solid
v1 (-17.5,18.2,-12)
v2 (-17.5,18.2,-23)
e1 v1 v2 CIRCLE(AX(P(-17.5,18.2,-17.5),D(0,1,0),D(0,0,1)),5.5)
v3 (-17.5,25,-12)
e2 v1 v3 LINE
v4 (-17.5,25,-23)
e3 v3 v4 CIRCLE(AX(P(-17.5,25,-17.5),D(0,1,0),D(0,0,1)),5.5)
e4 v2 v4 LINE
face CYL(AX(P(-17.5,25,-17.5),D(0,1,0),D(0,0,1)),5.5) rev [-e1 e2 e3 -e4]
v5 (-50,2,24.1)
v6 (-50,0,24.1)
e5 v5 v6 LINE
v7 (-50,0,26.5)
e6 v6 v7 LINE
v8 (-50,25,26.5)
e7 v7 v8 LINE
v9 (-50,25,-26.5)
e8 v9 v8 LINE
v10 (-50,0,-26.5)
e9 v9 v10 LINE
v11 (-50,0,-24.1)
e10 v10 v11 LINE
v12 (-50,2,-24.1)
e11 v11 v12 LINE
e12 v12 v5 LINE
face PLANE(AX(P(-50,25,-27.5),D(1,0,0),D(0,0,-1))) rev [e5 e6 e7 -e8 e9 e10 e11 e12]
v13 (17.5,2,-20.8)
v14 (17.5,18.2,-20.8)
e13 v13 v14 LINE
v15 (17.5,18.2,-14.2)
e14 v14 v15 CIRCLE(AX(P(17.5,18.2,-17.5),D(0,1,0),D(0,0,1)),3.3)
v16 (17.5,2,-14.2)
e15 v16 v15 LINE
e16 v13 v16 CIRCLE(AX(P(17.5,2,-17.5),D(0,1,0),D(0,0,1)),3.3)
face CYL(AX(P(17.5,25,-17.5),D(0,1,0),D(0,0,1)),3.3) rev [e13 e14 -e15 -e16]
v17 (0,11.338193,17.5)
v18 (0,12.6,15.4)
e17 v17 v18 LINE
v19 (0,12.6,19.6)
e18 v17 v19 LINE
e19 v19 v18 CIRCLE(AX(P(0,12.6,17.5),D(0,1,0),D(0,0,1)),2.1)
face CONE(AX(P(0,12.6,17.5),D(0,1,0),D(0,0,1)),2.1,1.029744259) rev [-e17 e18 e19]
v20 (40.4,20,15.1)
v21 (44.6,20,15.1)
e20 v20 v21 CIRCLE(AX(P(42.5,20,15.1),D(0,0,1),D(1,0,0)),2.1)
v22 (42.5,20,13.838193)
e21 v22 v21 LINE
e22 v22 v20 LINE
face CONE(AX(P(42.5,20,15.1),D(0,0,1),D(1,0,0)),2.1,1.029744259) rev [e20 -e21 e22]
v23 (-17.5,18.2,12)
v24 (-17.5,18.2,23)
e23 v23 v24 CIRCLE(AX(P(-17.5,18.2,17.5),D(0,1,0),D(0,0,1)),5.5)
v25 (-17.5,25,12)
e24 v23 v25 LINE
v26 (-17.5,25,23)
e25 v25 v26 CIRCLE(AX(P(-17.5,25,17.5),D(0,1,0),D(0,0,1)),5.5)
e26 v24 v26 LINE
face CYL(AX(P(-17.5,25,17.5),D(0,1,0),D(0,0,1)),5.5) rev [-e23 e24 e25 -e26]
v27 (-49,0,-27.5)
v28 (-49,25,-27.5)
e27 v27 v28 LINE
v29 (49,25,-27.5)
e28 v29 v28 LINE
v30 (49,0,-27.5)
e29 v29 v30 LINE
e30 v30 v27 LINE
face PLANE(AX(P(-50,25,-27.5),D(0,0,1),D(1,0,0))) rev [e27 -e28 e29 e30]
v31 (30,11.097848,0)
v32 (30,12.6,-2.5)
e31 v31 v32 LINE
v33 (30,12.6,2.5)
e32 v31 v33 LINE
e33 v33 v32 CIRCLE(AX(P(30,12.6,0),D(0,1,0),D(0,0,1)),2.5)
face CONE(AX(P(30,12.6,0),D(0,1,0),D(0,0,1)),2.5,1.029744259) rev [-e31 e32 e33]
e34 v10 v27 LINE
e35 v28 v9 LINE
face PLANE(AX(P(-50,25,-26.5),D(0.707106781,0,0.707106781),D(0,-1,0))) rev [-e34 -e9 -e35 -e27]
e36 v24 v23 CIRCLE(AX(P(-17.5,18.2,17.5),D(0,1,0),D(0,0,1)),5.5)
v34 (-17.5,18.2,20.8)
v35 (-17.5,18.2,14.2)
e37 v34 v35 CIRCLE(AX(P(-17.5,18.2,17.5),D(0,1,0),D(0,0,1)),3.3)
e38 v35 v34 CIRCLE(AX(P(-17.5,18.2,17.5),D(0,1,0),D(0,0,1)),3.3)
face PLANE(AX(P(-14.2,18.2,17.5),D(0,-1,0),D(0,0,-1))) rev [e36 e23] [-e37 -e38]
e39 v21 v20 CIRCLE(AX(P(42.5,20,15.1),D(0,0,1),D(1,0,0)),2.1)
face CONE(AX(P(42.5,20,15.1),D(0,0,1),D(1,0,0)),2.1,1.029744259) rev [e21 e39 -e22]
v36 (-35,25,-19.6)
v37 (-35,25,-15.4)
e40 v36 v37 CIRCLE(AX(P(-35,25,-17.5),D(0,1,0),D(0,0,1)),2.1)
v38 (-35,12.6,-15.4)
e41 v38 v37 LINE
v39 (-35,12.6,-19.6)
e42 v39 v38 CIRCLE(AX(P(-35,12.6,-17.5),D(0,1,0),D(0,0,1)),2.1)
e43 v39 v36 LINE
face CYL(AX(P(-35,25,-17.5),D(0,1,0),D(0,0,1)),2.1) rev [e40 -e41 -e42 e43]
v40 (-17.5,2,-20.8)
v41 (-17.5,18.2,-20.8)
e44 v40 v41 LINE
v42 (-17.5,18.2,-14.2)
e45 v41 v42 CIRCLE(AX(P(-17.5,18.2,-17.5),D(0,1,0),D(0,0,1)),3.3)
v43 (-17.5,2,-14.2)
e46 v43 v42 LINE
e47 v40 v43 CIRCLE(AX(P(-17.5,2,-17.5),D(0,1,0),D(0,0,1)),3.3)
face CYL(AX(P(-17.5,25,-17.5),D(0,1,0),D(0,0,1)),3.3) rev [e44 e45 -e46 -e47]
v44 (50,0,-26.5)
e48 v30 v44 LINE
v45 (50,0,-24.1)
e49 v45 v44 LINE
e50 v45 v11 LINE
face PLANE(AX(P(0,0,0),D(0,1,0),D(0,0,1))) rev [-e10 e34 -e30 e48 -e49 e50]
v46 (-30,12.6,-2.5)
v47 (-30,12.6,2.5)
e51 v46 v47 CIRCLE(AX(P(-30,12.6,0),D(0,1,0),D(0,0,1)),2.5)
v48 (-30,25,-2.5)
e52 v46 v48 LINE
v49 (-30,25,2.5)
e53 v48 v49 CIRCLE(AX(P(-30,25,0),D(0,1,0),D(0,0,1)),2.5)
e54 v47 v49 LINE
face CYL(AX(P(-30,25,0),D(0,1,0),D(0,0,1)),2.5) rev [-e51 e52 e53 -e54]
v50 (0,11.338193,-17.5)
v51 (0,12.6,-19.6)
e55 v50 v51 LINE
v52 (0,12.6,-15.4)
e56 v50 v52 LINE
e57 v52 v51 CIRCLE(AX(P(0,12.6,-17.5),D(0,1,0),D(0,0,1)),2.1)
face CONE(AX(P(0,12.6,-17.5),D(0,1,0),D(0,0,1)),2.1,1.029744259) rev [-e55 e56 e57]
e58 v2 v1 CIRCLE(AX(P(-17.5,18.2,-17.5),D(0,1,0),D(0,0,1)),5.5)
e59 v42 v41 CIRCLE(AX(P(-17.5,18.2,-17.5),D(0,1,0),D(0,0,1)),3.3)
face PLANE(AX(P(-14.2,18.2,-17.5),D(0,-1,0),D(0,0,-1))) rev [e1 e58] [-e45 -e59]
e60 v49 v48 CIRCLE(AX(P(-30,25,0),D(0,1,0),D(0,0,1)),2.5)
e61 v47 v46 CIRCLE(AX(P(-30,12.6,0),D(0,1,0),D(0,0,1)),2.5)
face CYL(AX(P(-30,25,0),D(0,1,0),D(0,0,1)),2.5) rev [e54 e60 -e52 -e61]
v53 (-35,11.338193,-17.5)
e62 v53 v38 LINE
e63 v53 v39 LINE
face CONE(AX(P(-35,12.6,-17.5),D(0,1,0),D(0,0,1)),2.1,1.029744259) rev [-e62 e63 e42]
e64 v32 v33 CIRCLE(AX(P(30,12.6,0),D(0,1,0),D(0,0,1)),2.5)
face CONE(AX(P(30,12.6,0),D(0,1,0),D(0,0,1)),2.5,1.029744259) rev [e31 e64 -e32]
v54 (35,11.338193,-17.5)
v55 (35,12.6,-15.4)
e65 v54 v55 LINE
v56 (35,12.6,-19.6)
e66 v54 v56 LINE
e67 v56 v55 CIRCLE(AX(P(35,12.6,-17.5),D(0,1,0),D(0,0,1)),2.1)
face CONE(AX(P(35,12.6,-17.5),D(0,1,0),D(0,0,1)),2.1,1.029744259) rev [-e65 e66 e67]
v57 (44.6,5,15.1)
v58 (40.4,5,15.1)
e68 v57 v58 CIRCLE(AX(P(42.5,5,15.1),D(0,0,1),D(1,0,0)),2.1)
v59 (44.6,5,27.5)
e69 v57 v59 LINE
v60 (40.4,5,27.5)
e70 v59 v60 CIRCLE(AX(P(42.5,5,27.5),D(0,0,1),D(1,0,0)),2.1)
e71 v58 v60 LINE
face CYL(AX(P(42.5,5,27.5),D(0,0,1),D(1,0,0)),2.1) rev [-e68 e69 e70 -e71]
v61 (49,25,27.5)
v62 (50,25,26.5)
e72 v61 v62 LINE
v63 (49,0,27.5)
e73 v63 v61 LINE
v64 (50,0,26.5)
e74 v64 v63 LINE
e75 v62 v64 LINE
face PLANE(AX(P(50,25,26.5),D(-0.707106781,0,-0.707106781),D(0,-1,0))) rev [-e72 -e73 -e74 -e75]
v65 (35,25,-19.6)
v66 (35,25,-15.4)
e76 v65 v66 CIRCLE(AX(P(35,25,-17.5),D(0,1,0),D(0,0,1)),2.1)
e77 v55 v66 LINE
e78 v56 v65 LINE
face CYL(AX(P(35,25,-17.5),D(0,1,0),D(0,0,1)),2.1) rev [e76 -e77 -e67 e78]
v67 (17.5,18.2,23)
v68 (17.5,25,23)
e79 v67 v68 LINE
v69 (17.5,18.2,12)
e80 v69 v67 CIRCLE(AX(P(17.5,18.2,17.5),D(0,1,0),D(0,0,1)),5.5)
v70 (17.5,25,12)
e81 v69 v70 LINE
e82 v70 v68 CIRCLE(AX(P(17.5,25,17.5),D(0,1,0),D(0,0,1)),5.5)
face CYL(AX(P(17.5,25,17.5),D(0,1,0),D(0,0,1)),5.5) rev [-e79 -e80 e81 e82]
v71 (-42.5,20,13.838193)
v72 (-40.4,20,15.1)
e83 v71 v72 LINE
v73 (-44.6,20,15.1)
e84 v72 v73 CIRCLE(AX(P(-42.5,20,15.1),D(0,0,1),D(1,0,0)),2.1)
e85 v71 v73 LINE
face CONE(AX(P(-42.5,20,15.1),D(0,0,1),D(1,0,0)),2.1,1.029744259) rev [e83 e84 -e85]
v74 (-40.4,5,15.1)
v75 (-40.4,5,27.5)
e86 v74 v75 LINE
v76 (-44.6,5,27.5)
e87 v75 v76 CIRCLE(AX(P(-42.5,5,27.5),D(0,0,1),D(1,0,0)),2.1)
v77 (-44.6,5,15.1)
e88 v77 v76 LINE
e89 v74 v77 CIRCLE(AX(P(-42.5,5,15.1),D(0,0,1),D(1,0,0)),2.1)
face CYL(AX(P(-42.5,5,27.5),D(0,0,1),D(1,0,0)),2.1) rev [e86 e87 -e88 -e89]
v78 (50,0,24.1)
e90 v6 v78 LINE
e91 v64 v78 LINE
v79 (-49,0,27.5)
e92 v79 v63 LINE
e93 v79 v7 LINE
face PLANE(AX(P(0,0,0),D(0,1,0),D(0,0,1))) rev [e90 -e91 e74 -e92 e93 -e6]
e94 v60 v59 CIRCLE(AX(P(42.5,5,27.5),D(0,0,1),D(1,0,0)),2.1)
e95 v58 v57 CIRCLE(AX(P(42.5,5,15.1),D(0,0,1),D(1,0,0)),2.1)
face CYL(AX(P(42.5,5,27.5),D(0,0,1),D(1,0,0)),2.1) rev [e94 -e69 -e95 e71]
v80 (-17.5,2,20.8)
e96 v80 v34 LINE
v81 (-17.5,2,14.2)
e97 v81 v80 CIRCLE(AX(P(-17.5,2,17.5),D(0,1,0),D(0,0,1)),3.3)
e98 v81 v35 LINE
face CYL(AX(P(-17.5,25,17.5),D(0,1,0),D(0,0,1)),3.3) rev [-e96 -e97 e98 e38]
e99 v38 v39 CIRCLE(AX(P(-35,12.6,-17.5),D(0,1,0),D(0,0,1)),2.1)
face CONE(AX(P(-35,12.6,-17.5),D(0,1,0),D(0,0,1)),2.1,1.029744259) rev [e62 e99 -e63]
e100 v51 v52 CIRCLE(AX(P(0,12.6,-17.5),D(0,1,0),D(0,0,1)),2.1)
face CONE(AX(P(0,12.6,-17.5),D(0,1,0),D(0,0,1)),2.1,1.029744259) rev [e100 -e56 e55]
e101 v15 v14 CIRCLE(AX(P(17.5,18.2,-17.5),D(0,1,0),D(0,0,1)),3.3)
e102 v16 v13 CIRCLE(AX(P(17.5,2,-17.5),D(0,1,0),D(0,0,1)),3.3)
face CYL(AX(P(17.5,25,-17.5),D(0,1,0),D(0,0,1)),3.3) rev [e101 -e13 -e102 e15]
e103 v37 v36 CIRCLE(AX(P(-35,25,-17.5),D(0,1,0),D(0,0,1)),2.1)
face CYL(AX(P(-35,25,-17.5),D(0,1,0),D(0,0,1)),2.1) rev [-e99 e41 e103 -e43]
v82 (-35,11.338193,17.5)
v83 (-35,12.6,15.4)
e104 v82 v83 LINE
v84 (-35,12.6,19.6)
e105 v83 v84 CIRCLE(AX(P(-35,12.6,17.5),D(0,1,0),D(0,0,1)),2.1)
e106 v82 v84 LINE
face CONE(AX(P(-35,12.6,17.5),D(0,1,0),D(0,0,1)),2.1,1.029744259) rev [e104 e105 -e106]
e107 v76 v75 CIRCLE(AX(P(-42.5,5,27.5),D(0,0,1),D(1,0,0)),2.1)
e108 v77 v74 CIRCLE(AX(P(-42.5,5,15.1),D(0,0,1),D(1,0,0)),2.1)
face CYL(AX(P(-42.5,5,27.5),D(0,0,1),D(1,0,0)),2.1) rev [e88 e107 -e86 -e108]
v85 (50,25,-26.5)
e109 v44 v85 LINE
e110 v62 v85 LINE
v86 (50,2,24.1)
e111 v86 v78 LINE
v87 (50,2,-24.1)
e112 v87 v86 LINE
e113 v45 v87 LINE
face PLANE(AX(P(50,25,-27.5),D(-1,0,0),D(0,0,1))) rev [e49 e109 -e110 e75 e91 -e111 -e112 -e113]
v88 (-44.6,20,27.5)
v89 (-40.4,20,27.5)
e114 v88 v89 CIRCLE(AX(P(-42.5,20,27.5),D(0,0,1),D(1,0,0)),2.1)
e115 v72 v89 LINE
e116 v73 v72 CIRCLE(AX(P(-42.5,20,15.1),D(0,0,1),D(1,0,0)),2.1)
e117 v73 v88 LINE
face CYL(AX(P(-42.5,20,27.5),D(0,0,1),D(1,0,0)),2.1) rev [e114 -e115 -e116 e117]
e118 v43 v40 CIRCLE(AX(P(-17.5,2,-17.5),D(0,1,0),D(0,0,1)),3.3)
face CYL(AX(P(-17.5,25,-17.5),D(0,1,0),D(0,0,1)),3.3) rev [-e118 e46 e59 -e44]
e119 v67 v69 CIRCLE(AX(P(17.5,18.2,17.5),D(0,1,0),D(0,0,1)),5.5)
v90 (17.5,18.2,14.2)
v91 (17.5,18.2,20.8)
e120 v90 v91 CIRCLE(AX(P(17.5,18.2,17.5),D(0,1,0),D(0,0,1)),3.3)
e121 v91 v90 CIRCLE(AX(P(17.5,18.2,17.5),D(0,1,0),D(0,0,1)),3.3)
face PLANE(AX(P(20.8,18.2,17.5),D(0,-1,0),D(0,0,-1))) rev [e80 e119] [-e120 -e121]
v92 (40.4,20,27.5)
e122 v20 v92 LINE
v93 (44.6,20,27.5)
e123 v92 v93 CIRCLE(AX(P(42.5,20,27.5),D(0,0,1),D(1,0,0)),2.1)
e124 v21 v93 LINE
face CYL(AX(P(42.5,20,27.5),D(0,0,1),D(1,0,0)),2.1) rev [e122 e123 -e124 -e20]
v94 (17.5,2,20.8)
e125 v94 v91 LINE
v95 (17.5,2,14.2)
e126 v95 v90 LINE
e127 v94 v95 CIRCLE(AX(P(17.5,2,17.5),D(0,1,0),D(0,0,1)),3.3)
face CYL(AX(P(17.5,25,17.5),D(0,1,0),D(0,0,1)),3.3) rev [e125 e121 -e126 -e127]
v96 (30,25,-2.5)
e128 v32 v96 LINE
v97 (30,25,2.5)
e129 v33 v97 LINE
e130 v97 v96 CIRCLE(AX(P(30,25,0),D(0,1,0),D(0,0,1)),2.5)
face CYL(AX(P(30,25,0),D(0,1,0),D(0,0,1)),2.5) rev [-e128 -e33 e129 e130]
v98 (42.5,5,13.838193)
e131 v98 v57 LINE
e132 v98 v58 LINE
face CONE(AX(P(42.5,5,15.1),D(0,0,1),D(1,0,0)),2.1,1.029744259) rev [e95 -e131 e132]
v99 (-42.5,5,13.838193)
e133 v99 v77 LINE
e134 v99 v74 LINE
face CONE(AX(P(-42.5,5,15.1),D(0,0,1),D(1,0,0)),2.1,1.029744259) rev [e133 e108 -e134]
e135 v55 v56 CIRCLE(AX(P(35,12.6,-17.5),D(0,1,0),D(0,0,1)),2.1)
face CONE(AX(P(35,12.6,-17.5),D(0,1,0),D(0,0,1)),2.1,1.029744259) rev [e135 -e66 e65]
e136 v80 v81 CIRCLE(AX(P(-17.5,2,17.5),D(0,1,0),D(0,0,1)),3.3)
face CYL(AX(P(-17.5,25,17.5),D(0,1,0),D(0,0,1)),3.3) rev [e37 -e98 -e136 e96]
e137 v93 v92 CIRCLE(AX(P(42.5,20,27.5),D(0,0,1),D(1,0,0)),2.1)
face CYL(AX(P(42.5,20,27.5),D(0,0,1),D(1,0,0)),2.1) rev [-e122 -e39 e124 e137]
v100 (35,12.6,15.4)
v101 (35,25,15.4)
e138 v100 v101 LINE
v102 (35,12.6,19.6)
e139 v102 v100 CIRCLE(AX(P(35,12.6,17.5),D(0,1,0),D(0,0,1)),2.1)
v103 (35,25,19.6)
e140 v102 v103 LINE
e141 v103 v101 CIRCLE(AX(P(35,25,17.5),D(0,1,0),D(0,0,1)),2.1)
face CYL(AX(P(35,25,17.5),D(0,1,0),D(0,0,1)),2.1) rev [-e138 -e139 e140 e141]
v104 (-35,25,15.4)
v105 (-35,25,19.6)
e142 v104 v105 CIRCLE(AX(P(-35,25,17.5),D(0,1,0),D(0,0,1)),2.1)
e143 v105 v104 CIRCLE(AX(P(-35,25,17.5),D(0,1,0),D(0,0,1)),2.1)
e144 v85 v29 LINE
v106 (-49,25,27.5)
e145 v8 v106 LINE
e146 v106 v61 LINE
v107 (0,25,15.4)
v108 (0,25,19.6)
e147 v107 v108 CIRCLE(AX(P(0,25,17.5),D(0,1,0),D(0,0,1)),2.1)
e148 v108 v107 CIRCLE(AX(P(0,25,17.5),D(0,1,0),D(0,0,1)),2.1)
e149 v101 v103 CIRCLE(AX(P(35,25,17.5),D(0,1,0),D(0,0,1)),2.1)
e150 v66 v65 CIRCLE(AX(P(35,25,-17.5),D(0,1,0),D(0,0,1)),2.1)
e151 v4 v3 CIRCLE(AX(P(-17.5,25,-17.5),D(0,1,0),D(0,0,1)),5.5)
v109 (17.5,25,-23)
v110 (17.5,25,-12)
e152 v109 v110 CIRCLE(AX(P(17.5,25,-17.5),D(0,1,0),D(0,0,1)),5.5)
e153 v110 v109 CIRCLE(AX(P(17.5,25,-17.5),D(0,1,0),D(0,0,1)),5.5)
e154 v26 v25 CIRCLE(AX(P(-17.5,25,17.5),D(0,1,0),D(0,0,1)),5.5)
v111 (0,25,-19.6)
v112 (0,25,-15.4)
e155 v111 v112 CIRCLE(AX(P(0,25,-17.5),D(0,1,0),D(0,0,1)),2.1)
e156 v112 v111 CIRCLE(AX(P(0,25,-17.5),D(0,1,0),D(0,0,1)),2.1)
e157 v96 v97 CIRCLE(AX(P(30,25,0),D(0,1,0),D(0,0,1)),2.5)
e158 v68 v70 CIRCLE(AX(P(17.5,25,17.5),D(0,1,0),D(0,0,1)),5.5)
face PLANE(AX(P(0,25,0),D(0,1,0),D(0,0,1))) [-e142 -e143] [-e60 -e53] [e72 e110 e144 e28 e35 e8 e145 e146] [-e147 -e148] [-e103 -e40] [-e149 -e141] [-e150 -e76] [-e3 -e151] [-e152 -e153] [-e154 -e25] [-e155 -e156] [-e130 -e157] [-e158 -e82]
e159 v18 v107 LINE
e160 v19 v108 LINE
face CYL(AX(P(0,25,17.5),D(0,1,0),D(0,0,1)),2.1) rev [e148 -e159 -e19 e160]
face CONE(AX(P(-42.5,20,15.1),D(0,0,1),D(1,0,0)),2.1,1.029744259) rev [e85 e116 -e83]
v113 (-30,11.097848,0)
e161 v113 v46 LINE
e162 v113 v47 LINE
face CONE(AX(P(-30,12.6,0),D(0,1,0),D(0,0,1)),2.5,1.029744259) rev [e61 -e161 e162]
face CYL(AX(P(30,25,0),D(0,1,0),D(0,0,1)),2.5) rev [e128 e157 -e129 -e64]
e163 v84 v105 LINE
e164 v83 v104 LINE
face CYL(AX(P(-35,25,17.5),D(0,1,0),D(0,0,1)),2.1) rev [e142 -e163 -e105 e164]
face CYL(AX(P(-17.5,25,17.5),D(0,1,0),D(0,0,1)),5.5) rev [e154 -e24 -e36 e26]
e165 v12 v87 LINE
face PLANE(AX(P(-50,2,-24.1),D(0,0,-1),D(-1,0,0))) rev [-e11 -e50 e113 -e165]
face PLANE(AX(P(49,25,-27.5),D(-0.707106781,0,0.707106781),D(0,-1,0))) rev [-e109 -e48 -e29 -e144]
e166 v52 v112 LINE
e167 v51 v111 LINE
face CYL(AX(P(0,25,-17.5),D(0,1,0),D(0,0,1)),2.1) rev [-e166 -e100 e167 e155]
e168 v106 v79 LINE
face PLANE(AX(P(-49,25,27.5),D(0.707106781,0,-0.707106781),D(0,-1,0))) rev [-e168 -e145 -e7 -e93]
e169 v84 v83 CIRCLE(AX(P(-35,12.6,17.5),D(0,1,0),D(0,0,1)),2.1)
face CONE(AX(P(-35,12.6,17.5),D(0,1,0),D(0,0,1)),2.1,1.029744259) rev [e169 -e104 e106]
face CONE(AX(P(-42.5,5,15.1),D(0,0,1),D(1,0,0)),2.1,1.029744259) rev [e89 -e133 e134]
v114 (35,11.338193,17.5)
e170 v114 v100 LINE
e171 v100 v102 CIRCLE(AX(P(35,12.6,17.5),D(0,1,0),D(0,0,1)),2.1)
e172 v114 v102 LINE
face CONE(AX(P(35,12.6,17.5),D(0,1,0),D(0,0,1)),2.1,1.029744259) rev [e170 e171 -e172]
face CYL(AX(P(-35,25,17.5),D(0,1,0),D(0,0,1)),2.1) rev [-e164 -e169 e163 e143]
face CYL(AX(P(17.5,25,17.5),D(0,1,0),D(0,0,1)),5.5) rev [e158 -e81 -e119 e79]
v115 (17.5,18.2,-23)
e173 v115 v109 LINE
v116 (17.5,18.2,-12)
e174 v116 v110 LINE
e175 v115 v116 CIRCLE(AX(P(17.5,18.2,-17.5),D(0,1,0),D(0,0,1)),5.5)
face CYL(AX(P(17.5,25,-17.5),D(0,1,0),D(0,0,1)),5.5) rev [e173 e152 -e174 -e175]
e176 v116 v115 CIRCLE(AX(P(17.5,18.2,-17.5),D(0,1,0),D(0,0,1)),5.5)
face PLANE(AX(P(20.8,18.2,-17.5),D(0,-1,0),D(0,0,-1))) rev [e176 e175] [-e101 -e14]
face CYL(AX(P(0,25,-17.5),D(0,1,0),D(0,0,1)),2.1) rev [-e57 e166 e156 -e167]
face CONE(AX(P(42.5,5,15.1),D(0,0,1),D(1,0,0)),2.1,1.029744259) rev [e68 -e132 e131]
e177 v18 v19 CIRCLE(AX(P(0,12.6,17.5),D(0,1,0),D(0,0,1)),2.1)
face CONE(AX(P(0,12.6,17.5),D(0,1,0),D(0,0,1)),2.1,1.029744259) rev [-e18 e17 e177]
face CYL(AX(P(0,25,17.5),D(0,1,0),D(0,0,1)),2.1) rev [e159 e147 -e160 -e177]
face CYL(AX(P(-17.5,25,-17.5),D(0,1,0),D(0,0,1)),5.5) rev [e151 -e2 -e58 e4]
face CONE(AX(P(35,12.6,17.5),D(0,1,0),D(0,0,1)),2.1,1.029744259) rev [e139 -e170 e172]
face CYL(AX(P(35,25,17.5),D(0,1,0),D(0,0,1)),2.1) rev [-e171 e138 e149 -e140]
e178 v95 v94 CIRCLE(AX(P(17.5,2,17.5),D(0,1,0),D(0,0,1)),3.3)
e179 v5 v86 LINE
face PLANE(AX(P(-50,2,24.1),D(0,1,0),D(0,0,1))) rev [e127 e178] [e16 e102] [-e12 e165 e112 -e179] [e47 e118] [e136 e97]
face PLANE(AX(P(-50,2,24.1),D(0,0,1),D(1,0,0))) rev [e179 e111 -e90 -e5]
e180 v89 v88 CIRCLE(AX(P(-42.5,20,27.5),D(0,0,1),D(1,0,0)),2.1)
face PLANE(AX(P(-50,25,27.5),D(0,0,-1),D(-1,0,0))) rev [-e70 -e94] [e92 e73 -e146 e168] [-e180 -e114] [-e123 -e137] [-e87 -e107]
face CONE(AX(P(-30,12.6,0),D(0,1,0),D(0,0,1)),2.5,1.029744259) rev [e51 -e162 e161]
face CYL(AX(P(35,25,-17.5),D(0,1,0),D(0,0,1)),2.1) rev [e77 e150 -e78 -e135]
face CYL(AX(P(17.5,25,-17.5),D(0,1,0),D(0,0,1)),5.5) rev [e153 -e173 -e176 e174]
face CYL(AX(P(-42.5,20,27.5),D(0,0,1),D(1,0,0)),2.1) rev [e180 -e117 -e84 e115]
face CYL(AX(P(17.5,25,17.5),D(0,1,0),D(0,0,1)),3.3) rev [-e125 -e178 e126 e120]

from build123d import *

# Parameters (mm, degrees)
SKETCH_1_W                = 100
SKETCH_1_H                = 55
EXTRUDE_1_DEPTH           = 25
SKETCH_2_W                = 48.2
SKETCH_2_H                = 4
CUT_EXTRUDE_1_DEPTH       = 107.682941467
HOLE_WIZARD_M5_1_D        = 4.2
HOLE_WIZARD_M5_1_DEPTH    = 12.4
HOLE_WIZARD_M5_1_TIP      = 1.2618073
CHAMFER_1_SIZE            = 1
HOLE_WIZARD_0_D           = 6.6
HOLE_WIZARD_0_DEPTH       = 40
HOLE_WIZARD_0_CBORE_D     = 11
HOLE_WIZARD_0_CBORE_DEPTH = 6.8
HOLE_WIZARD_0_TIP         = 1.982840043
HOLE_WIZARD_M5_2_D        = 4.2
HOLE_WIZARD_M5_2_DEPTH    = 12.4
HOLE_WIZARD_M5_2_TIP      = 1.2618073
MM_1_D                    = 5
MM_1_DEPTH                = 12.4
MM_1_TIP                  = 1.502151548


with BuildPart() as part:
    # 草图1 → 凸台-拉伸1 (new body)
    with BuildSketch(Plane(origin=(0, 0, 0), x_dir=(1, 0, 0), z_dir=(0, 1, 0))):
        Rectangle(SKETCH_1_W, SKETCH_1_H)
    extrude(amount=EXTRUDE_1_DEPTH)

    # 草图2 → 切除-拉伸1 (cut, through all)
    with BuildSketch(Plane(origin=(50, 0, 0), x_dir=(0, 0, -1), z_dir=(1, 0, 0))):
        Rectangle(SKETCH_2_W, SKETCH_2_H)
    extrude(amount=-CUT_EXTRUDE_1_DEPTH, mode=Mode.SUBTRACT)

    # M5 螺纹孔1
    with Locations(Plane.XY.offset(27.5)):
        with Locations((42.5, 20), (42.5, 5), (-42.5, 20), (-42.5, 5)):
            Hole(HOLE_WIZARD_M5_1_D / 2, depth=HOLE_WIZARD_M5_1_DEPTH)
            with Locations((0, 0, -(HOLE_WIZARD_M5_1_DEPTH + HOLE_WIZARD_M5_1_TIP / 2))):  # 118° drill point
                Cone(0, HOLE_WIZARD_M5_1_D / 2, HOLE_WIZARD_M5_1_TIP, mode=Mode.SUBTRACT)

    # 倒角1
    chamfer_1_edges = [part.edges().sort_by_distance(p)[0] for p in [
        (50, 12.5, 27.5),
        (-50, 12.5, 27.5),
        (-50, 12.5, -27.5),
        (50, 12.5, -27.5),
    ]]
    chamfer(chamfer_1_edges, length=CHAMFER_1_SIZE)

    # 打孔尺寸(%根据)内六角圆柱头螺钉的类型0
    with Locations(Plane(origin=(0, 25, 0), x_dir=(1, 0, 0), z_dir=(0, 1, 0))):
        with Locations((-17.499999996, 17.499999996), (17.500000004, 17.499999996), (-17.499999996, -17.500000004), (17.500000004, -17.500000004)):
            CounterBoreHole(HOLE_WIZARD_0_D / 2, HOLE_WIZARD_0_CBORE_D / 2, HOLE_WIZARD_0_CBORE_DEPTH, depth=HOLE_WIZARD_0_DEPTH)
            with Locations((0, 0, -(HOLE_WIZARD_0_DEPTH + HOLE_WIZARD_0_TIP / 2))):  # 118° drill point
                Cone(0, HOLE_WIZARD_0_D / 2, HOLE_WIZARD_0_TIP, mode=Mode.SUBTRACT)

    # M5 螺纹孔2
    with Locations(Plane(origin=(0, 25, 0), x_dir=(1, 0, 0), z_dir=(0, 1, 0))):
        with Locations((-35, 17.5), (-35, -17.5), (35, 17.5), (35, -17.5), (0, 17.5), (0, -17.5)):
            Hole(HOLE_WIZARD_M5_2_D / 2, depth=HOLE_WIZARD_M5_2_DEPTH)
            with Locations((0, 0, -(HOLE_WIZARD_M5_2_DEPTH + HOLE_WIZARD_M5_2_TIP / 2))):  # 118° drill point
                Cone(0, HOLE_WIZARD_M5_2_D / 2, HOLE_WIZARD_M5_2_TIP, mode=Mode.SUBTRACT)

    # 大小mm 暗销孔1
    with Locations(Plane(origin=(0, 25, 0), x_dir=(1, 0, 0), z_dir=(0, 1, 0))):
        with Locations((-30, 0), (30, 0)):
            Hole(MM_1_D / 2, depth=MM_1_DEPTH)
            with Locations((0, 0, -(MM_1_DEPTH + MM_1_TIP / 2))):  # 118° drill point
                Cone(0, MM_1_D / 2, MM_1_TIP, mode=Mode.SUBTRACT)


solid = part.part
